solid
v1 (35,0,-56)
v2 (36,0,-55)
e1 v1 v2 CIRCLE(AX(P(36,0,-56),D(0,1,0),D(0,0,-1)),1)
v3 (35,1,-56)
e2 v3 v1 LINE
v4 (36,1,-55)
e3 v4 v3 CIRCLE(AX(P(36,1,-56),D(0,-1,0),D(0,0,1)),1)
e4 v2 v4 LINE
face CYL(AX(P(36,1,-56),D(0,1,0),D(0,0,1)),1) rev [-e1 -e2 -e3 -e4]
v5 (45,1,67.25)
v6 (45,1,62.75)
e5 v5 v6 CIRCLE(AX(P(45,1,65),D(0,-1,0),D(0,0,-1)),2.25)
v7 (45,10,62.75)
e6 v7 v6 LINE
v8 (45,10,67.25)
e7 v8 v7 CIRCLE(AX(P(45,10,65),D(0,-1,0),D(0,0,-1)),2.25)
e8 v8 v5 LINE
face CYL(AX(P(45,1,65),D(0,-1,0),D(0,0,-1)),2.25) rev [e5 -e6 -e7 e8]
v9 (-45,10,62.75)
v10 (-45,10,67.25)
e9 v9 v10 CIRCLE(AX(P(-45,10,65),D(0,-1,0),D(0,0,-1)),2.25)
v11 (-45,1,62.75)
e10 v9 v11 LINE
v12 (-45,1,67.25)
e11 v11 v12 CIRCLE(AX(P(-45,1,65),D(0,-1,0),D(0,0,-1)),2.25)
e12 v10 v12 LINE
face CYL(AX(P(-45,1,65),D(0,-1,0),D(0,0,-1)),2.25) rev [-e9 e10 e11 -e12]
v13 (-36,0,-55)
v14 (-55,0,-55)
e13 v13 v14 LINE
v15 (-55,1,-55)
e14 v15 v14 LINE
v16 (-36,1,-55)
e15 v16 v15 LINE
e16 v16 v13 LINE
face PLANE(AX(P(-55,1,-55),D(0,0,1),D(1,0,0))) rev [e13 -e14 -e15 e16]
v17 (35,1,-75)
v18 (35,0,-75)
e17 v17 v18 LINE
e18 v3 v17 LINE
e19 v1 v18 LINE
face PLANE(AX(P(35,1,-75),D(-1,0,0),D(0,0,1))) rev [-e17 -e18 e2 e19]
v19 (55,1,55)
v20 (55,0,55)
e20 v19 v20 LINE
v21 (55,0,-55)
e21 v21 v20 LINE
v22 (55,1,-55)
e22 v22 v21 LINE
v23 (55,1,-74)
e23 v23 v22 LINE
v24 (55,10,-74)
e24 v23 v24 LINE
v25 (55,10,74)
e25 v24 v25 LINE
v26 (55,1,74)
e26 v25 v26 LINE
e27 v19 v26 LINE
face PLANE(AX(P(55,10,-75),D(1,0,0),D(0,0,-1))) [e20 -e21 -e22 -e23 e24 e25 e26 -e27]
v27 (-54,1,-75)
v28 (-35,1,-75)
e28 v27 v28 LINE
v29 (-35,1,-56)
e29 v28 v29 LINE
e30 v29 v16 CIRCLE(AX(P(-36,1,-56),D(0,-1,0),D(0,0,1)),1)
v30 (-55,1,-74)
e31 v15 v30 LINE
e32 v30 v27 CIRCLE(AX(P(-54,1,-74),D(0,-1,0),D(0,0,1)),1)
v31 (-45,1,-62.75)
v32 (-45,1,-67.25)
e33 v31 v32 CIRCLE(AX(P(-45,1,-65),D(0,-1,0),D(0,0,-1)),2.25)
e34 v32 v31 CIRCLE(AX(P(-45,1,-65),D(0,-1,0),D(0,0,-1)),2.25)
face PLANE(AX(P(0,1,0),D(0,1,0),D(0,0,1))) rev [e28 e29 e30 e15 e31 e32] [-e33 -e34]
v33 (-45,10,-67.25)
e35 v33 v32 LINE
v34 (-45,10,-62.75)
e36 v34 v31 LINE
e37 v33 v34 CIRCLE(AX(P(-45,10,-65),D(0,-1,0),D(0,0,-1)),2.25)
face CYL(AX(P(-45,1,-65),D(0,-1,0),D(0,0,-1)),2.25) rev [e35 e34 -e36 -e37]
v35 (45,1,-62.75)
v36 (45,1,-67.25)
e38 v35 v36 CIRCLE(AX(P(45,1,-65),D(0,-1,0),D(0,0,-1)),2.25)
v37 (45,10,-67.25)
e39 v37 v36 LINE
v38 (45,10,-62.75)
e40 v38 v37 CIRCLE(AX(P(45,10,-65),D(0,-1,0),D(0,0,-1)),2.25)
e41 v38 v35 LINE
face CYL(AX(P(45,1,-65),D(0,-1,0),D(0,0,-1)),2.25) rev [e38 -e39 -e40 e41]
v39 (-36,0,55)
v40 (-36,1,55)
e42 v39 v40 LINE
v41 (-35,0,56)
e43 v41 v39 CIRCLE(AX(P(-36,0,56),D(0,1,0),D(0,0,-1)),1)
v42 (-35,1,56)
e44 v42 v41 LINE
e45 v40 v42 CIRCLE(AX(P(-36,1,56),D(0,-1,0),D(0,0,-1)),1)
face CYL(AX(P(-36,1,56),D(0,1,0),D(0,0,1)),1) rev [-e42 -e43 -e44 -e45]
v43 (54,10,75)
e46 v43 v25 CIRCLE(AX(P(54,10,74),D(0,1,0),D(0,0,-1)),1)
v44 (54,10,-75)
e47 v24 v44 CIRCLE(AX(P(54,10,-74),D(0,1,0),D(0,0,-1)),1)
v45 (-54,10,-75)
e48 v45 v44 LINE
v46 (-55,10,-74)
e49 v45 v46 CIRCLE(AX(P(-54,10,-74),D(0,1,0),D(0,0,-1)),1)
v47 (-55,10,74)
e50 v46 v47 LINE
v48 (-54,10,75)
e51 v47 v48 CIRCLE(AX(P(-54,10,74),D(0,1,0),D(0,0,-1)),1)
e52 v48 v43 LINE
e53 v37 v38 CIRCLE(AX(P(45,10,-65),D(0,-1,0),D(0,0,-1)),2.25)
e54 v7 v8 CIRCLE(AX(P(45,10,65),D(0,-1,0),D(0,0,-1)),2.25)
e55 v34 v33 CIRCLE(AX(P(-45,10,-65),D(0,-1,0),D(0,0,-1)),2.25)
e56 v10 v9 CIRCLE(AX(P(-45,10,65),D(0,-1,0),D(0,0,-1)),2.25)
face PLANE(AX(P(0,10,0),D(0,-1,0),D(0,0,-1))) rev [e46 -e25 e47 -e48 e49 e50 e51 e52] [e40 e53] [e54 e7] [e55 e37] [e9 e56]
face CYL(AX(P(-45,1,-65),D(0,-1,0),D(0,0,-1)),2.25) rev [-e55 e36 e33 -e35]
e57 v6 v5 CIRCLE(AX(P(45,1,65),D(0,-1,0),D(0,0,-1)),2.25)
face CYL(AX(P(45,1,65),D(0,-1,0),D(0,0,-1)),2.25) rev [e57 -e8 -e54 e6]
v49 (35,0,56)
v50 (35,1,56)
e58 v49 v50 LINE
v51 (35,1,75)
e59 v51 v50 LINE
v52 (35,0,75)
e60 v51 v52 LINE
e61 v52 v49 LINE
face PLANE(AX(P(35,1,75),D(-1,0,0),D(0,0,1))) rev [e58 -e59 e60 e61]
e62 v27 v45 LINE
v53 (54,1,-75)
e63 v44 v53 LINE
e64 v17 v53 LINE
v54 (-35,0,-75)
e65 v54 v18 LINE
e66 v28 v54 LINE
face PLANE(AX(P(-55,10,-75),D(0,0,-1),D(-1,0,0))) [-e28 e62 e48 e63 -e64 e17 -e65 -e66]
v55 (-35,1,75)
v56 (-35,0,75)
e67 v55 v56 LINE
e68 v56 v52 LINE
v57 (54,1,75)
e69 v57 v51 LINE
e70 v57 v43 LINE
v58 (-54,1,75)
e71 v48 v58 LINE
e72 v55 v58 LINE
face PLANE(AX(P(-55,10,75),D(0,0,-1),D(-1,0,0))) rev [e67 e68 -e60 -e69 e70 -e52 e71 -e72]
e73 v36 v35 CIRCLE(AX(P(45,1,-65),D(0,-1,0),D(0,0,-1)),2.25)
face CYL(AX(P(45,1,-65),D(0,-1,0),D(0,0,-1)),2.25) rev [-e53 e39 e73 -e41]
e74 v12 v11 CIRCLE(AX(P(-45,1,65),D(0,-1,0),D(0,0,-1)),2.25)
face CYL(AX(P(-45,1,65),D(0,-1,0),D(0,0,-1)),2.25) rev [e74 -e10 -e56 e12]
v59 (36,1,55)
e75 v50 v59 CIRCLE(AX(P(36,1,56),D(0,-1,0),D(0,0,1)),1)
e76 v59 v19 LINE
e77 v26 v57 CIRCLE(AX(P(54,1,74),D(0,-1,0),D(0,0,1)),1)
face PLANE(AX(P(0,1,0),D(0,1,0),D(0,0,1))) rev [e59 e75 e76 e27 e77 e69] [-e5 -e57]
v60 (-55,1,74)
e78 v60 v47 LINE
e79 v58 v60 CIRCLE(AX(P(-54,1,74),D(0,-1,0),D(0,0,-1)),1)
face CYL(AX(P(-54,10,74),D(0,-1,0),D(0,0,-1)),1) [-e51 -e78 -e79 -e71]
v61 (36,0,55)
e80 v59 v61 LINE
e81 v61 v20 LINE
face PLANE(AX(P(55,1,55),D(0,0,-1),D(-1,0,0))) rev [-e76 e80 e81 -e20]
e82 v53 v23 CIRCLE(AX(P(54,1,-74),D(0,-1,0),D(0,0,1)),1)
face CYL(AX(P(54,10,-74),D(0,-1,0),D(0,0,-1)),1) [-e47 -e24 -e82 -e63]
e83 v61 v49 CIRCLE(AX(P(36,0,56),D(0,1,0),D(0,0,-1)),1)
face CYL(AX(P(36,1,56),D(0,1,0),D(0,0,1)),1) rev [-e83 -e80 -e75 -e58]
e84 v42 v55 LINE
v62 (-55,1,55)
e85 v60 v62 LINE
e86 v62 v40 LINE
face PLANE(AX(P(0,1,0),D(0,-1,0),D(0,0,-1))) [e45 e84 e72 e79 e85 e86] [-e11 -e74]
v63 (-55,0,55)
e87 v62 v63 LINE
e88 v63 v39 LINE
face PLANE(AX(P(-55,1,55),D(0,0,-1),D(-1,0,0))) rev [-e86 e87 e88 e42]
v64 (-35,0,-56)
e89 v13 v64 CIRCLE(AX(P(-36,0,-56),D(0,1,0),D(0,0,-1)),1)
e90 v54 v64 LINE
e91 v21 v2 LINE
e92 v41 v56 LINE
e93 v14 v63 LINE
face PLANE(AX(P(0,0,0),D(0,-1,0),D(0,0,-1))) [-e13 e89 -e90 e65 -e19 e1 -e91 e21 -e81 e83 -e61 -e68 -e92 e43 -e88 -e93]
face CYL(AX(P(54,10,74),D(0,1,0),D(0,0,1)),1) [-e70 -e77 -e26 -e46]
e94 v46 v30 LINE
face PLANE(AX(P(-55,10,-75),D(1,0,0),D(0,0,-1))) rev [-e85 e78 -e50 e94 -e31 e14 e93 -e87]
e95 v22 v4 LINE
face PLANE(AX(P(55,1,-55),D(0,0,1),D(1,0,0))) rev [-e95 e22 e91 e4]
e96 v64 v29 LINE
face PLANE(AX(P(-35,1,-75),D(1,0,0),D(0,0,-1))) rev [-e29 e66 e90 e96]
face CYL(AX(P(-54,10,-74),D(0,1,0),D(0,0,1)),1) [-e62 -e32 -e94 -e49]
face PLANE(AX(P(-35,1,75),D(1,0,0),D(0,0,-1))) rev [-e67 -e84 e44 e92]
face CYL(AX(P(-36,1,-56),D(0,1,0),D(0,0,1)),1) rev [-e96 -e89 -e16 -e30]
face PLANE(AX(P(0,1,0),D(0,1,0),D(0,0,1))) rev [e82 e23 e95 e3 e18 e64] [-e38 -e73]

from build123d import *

# Parameters (mm, degrees)
SKETCH1_W                  = 110
SKETCH1_H                  = 150
BOSS_EXTRUDE1_DEPTH        = 10
SKETCH2_W                  = 20
SKETCH2_H                  = 20
CUT_EXTRUDE1_DEPTH         = 1
F_4_5_4_5_DIAMETER_HOLE1_D = 4.5
FILLET1_R                  = 1
FILLET2_R                  = 1


with BuildPart() as part:
    # Sketch1 → Boss-Extrude1 (new body)
    with BuildSketch(Plane(origin=(0, 0, 0), x_dir=(1, 0, 0), z_dir=(0, 1, 0))):
        Rectangle(SKETCH1_W, SKETCH1_H)
    extrude(amount=BOSS_EXTRUDE1_DEPTH)

    # Sketch2 → Cut-Extrude1 (cut)
    with BuildSketch(Plane.XZ):
        with Locations((-45, 65)):
            Rectangle(SKETCH2_W, SKETCH2_H)
        with Locations((45, 65)):
            Rectangle(SKETCH2_W, SKETCH2_H)
        with Locations((45, -65)):
            Rectangle(SKETCH2_W, SKETCH2_H)
        with Locations((-45, -65)):
            Rectangle(SKETCH2_W, SKETCH2_H)
    extrude(amount=-CUT_EXTRUDE1_DEPTH, mode=Mode.SUBTRACT)

    # Ø4.5 (4.5) Diameter Hole1 (through all)
    with Locations(Plane(origin=(0, 1, 0), x_dir=(-1, 0, 0), z_dir=(0, -1, 0))):
        with Locations((-45, 65), (45, 65), (45, -65), (-45, -65)):
            Hole(F_4_5_4_5_DIAMETER_HOLE1_D / 2)

    # Fillet1
    fillet1_edges = [part.edges().sort_by_distance(p)[0] for p in [
        (-35, 0.5, -55),
        (35, 0.5, -55),
        (35, 0.5, 55),
        (-35, 0.5, 55),
    ]]
    fillet(fillet1_edges, radius=FILLET1_R)

    # Fillet2
    fillet2_edges = [part.edges().sort_by_distance(p)[0] for p in [
        (-55, 5.5, -75),
        (-55, 5.5, 75),
        (55, 5.5, 75),
        (55, 5.5, -75),
    ]]
    fillet(fillet2_edges, radius=FILLET2_R)


solid = part.part
